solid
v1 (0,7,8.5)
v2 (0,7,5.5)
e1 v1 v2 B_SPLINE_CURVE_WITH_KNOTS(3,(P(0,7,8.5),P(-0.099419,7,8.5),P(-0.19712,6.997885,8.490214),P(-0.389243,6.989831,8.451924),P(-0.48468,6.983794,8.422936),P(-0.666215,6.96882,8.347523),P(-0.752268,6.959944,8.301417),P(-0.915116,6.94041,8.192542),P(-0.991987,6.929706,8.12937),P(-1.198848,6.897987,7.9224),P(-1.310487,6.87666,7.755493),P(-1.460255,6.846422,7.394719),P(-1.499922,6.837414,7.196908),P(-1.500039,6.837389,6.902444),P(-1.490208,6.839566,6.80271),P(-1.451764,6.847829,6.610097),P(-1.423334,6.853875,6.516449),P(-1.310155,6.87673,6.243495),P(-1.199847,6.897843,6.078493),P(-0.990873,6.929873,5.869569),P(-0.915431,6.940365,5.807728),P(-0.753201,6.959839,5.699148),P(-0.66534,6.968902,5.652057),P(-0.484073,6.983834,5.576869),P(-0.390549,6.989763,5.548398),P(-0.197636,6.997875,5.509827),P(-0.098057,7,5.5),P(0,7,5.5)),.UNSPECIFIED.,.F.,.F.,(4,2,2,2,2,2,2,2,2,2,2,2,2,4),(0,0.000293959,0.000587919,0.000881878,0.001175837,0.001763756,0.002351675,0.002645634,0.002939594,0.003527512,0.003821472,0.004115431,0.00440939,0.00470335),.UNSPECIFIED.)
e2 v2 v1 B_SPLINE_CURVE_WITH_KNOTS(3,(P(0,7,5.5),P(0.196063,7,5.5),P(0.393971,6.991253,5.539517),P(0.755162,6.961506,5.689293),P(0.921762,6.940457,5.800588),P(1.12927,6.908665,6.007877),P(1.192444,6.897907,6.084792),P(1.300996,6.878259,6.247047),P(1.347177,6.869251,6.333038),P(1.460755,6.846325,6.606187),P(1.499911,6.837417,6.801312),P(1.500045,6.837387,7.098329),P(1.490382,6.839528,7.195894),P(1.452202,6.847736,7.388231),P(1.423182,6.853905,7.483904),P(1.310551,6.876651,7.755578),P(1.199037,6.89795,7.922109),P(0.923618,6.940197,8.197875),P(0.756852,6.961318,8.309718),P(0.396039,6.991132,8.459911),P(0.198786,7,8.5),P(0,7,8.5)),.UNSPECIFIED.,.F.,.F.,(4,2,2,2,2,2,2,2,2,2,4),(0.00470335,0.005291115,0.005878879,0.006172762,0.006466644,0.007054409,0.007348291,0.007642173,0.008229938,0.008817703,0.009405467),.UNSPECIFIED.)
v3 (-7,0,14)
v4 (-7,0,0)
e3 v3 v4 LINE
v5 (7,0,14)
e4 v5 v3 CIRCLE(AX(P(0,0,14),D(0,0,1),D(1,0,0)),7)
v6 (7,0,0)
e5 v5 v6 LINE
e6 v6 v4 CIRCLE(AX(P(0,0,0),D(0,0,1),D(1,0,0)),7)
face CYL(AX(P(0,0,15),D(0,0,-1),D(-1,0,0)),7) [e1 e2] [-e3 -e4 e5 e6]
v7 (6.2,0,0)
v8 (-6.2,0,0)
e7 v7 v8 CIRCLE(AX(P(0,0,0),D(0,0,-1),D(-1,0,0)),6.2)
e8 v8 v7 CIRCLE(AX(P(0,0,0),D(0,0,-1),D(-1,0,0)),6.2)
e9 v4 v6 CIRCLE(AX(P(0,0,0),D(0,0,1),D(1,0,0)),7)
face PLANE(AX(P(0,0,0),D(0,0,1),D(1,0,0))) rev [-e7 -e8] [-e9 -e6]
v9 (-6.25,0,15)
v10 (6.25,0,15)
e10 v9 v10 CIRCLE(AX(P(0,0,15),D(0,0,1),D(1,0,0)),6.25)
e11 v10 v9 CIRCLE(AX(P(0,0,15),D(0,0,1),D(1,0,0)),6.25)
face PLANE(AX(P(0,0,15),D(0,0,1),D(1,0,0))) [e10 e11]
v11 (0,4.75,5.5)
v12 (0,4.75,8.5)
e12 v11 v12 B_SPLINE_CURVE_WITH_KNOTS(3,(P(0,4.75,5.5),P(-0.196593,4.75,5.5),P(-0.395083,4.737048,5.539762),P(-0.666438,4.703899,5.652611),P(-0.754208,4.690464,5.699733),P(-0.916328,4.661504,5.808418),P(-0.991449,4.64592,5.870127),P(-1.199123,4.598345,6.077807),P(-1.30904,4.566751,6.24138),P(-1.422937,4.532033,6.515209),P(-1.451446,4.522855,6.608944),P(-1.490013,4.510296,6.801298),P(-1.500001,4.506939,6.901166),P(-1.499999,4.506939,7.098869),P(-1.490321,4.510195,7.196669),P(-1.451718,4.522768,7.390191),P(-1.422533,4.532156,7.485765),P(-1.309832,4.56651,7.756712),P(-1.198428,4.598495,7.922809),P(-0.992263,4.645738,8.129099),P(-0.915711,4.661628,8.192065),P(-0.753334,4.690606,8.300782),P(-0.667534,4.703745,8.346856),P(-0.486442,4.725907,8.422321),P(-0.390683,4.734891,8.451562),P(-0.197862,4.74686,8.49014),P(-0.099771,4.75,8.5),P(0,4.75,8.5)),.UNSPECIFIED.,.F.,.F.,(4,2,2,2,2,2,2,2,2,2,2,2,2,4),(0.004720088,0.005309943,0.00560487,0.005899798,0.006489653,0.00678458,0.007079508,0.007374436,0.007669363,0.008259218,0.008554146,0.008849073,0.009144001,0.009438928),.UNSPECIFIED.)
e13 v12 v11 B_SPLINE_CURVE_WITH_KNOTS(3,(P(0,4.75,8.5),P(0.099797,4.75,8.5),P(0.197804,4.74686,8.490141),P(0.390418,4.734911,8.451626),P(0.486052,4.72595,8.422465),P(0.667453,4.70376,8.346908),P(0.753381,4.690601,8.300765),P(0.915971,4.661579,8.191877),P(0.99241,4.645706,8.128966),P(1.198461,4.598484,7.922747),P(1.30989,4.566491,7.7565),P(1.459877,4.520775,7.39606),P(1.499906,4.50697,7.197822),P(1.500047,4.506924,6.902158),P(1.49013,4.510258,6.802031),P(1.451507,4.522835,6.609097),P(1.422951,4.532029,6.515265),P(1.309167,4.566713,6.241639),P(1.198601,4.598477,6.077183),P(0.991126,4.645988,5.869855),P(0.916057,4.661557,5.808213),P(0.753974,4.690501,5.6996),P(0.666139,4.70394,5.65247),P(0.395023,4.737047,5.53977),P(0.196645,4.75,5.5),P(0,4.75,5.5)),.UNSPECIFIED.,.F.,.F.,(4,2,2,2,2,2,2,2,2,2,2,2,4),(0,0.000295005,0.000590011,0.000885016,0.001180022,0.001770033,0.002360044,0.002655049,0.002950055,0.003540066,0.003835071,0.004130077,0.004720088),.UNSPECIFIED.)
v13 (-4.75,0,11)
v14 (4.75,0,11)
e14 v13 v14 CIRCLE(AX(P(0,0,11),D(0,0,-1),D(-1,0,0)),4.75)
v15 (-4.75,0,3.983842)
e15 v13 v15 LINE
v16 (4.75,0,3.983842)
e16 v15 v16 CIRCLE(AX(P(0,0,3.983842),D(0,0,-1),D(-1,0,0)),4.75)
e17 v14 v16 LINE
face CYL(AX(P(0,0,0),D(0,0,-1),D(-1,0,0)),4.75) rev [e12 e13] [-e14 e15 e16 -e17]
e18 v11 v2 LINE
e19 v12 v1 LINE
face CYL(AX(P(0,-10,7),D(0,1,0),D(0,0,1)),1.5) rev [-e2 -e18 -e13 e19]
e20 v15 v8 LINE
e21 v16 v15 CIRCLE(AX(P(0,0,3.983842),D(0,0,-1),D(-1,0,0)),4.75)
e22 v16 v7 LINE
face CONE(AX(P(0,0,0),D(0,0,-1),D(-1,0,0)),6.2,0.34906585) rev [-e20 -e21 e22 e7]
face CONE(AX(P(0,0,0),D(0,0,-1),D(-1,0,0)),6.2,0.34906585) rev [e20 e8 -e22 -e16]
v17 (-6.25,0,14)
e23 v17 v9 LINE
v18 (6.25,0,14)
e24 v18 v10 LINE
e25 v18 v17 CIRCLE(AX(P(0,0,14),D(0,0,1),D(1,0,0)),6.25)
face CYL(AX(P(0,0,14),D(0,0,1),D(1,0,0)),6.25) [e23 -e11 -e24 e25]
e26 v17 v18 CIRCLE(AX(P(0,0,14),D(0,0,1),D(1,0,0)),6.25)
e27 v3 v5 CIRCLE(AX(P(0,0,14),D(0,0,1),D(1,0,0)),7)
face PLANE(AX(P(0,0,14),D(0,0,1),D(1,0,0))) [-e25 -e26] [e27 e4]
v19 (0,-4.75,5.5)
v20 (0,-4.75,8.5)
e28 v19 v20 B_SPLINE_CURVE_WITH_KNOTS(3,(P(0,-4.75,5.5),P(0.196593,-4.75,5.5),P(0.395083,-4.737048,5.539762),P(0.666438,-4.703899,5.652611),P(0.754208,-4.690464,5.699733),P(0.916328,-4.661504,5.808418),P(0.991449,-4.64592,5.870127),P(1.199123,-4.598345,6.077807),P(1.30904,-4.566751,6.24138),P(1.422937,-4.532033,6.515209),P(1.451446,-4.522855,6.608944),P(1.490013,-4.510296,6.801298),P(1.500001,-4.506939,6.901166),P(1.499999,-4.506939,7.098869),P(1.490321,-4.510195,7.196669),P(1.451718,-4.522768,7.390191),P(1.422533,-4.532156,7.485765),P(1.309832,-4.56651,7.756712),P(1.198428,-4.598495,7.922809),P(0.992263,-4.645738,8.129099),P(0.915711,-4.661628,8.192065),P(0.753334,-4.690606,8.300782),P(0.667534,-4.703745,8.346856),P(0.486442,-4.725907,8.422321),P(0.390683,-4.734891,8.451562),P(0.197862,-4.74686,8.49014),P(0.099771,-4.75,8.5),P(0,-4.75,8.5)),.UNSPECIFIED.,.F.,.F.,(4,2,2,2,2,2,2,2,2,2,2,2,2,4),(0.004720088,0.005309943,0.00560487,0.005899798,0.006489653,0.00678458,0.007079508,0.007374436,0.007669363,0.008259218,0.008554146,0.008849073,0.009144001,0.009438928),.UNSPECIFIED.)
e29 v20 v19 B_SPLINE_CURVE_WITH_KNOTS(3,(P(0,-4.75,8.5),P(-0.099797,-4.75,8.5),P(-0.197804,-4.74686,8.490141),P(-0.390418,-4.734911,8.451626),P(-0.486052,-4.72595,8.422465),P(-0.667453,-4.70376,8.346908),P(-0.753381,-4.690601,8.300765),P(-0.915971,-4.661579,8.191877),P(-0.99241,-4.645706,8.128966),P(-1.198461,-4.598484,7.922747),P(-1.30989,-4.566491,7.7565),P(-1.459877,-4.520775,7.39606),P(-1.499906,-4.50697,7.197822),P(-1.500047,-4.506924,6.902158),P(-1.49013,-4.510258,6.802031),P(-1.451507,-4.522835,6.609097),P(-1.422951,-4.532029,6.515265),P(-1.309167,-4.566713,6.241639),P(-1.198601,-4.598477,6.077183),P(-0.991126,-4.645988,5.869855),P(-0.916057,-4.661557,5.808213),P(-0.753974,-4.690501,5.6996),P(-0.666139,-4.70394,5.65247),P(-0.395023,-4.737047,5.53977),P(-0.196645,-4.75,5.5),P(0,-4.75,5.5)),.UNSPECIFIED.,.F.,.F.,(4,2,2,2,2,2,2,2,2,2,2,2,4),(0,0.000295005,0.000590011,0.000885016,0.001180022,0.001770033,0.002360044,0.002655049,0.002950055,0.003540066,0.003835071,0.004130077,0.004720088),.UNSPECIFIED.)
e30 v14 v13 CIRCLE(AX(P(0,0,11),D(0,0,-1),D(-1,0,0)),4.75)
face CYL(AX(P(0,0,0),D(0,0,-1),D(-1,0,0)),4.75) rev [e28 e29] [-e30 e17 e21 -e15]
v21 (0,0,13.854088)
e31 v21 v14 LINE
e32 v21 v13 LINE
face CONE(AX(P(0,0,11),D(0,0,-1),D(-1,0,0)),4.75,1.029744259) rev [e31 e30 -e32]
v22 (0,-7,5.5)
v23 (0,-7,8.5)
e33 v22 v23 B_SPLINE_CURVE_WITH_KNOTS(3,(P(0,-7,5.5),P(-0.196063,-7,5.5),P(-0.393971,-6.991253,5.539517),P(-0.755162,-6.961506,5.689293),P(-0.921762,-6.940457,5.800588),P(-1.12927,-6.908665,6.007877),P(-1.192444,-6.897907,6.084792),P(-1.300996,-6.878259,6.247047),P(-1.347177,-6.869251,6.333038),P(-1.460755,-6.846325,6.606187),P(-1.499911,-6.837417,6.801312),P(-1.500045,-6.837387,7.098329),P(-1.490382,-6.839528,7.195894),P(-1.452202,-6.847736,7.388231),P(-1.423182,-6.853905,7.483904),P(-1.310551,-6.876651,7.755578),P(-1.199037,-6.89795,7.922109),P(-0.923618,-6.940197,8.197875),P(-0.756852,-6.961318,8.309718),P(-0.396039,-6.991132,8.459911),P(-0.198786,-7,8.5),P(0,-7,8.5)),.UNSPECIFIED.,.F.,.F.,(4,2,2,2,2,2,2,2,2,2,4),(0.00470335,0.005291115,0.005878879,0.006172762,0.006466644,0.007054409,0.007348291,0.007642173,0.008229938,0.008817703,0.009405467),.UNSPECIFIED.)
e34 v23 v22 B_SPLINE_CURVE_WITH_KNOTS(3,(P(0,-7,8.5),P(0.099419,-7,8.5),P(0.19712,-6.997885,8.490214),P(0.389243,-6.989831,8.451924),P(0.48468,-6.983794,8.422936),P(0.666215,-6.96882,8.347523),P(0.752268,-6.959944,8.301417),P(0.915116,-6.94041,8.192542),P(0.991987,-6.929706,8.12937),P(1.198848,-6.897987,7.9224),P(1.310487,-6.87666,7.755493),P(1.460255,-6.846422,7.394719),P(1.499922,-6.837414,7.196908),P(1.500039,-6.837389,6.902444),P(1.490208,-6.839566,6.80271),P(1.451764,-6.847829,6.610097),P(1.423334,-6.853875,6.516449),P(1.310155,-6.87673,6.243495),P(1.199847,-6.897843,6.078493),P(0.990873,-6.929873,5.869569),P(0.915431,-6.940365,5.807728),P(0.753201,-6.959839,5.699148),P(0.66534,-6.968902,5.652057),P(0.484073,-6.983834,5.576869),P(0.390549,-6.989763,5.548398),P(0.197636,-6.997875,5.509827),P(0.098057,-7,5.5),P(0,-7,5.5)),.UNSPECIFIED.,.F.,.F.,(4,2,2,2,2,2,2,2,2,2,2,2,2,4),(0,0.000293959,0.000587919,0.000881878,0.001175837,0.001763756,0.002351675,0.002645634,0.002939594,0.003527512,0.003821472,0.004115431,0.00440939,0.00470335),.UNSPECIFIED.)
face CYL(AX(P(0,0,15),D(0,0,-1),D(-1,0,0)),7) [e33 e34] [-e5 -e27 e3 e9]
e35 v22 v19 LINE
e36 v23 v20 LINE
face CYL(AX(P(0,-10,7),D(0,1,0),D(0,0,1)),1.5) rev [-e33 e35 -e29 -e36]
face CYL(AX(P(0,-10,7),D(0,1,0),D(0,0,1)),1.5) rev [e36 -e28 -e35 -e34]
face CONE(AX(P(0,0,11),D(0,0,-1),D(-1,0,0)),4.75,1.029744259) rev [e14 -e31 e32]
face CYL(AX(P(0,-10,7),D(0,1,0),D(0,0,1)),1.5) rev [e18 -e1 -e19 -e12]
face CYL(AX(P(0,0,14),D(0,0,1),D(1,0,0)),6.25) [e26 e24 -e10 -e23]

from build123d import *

# Parameters (mm, degrees)
SKETCH1_R                      = 7
BOSS_EXTRUDE1_DEPTH            = 15
CUT_EXTRUDE1_START             = -1
SKETCH2_R                      = 7
SKETCH2_R_2                    = 6.25
CUT_EXTRUDE1_DEPTH             = 1
F_9_5_9_5_DIAMETER_HOLE1_D     = 9.5
F_9_5_9_5_DIAMETER_HOLE1_DEPTH = 11
F_9_5_9_5_DIAMETER_HOLE1_TIP   = 2.85408794
SKETCH4_R                      = 6.2
CUT_EXTRUDE2_DEPTH             = 5
CUT_EXTRUDE2_DRAFT             = -20
SKETCH5_R                      = 1.5
CUT_EXTRUDE3_DEPTH             = 10


with BuildPart() as part:
    # Sketch1 → Boss-Extrude1 (new body)
    with BuildSketch(Plane.XY):
        Circle(SKETCH1_R)
    extrude(amount=BOSS_EXTRUDE1_DEPTH)

    # Sketch2 → Cut-Extrude1 (cut)
    with BuildSketch(Plane.XY.offset(15).offset(CUT_EXTRUDE1_START)):
        Circle(SKETCH2_R)
        Circle(SKETCH2_R_2, mode=Mode.SUBTRACT)
    extrude(amount=CUT_EXTRUDE1_DEPTH, mode=Mode.SUBTRACT)

    # Ø9.5 (9.5) Diameter Hole1
    with Locations(Plane(origin=(0, 0, 0), x_dir=(-1, 0, 0), z_dir=(0, 0, -1))):
        with Locations((0, 0)):
            Hole(F_9_5_9_5_DIAMETER_HOLE1_D / 2, depth=F_9_5_9_5_DIAMETER_HOLE1_DEPTH)
            with Locations((0, 0, -(F_9_5_9_5_DIAMETER_HOLE1_DEPTH + F_9_5_9_5_DIAMETER_HOLE1_TIP / 2))):  # 118° drill point
                Cone(0, F_9_5_9_5_DIAMETER_HOLE1_D / 2, F_9_5_9_5_DIAMETER_HOLE1_TIP, mode=Mode.SUBTRACT)


with BuildPart() as cut_extrude2_tool:
    # Sketch4 → Cut-Extrude2 (with draft: the straight prism first)
    with BuildSketch(Plane(origin=(0, 0, 0), x_dir=(-1, 0, 0), z_dir=(0, 0, -1))):
        Circle(SKETCH4_R)
    extrude(amount=-CUT_EXTRUDE2_DEPTH)
    # Cut-Extrude2: the draft: its side faces are tilted about the plane it starts from
    cut_extrude2_sides = [cut_extrude2_tool.faces().sort_by_distance(p)[0] for p in [
        (6.2, 0, 2.5),
    ]]
    draft(cut_extrude2_sides, Plane(origin=(0, 0, 0), x_dir=(-1, 0, 0), z_dir=(0, 0, -1)), CUT_EXTRUDE2_DRAFT)


with BuildPart() as part_1:
    add(part.part)

    # Cut-Extrude2: cut by cut_extrude2_tool
    add(cut_extrude2_tool.part, mode=Mode.SUBTRACT)

    # Sketch5 → Cut-Extrude3 (cut, symmetric)
    with BuildSketch(Plane(origin=(0, 0, 0), x_dir=(1, 0, 0), z_dir=(0, 1, 0))):
        with Locations(Location((0, -7, 0), (0, 0, 270))):
            Circle(SKETCH5_R)
    extrude(amount=CUT_EXTRUDE3_DEPTH, both=True, mode=Mode.SUBTRACT)


solid = part_1.part
